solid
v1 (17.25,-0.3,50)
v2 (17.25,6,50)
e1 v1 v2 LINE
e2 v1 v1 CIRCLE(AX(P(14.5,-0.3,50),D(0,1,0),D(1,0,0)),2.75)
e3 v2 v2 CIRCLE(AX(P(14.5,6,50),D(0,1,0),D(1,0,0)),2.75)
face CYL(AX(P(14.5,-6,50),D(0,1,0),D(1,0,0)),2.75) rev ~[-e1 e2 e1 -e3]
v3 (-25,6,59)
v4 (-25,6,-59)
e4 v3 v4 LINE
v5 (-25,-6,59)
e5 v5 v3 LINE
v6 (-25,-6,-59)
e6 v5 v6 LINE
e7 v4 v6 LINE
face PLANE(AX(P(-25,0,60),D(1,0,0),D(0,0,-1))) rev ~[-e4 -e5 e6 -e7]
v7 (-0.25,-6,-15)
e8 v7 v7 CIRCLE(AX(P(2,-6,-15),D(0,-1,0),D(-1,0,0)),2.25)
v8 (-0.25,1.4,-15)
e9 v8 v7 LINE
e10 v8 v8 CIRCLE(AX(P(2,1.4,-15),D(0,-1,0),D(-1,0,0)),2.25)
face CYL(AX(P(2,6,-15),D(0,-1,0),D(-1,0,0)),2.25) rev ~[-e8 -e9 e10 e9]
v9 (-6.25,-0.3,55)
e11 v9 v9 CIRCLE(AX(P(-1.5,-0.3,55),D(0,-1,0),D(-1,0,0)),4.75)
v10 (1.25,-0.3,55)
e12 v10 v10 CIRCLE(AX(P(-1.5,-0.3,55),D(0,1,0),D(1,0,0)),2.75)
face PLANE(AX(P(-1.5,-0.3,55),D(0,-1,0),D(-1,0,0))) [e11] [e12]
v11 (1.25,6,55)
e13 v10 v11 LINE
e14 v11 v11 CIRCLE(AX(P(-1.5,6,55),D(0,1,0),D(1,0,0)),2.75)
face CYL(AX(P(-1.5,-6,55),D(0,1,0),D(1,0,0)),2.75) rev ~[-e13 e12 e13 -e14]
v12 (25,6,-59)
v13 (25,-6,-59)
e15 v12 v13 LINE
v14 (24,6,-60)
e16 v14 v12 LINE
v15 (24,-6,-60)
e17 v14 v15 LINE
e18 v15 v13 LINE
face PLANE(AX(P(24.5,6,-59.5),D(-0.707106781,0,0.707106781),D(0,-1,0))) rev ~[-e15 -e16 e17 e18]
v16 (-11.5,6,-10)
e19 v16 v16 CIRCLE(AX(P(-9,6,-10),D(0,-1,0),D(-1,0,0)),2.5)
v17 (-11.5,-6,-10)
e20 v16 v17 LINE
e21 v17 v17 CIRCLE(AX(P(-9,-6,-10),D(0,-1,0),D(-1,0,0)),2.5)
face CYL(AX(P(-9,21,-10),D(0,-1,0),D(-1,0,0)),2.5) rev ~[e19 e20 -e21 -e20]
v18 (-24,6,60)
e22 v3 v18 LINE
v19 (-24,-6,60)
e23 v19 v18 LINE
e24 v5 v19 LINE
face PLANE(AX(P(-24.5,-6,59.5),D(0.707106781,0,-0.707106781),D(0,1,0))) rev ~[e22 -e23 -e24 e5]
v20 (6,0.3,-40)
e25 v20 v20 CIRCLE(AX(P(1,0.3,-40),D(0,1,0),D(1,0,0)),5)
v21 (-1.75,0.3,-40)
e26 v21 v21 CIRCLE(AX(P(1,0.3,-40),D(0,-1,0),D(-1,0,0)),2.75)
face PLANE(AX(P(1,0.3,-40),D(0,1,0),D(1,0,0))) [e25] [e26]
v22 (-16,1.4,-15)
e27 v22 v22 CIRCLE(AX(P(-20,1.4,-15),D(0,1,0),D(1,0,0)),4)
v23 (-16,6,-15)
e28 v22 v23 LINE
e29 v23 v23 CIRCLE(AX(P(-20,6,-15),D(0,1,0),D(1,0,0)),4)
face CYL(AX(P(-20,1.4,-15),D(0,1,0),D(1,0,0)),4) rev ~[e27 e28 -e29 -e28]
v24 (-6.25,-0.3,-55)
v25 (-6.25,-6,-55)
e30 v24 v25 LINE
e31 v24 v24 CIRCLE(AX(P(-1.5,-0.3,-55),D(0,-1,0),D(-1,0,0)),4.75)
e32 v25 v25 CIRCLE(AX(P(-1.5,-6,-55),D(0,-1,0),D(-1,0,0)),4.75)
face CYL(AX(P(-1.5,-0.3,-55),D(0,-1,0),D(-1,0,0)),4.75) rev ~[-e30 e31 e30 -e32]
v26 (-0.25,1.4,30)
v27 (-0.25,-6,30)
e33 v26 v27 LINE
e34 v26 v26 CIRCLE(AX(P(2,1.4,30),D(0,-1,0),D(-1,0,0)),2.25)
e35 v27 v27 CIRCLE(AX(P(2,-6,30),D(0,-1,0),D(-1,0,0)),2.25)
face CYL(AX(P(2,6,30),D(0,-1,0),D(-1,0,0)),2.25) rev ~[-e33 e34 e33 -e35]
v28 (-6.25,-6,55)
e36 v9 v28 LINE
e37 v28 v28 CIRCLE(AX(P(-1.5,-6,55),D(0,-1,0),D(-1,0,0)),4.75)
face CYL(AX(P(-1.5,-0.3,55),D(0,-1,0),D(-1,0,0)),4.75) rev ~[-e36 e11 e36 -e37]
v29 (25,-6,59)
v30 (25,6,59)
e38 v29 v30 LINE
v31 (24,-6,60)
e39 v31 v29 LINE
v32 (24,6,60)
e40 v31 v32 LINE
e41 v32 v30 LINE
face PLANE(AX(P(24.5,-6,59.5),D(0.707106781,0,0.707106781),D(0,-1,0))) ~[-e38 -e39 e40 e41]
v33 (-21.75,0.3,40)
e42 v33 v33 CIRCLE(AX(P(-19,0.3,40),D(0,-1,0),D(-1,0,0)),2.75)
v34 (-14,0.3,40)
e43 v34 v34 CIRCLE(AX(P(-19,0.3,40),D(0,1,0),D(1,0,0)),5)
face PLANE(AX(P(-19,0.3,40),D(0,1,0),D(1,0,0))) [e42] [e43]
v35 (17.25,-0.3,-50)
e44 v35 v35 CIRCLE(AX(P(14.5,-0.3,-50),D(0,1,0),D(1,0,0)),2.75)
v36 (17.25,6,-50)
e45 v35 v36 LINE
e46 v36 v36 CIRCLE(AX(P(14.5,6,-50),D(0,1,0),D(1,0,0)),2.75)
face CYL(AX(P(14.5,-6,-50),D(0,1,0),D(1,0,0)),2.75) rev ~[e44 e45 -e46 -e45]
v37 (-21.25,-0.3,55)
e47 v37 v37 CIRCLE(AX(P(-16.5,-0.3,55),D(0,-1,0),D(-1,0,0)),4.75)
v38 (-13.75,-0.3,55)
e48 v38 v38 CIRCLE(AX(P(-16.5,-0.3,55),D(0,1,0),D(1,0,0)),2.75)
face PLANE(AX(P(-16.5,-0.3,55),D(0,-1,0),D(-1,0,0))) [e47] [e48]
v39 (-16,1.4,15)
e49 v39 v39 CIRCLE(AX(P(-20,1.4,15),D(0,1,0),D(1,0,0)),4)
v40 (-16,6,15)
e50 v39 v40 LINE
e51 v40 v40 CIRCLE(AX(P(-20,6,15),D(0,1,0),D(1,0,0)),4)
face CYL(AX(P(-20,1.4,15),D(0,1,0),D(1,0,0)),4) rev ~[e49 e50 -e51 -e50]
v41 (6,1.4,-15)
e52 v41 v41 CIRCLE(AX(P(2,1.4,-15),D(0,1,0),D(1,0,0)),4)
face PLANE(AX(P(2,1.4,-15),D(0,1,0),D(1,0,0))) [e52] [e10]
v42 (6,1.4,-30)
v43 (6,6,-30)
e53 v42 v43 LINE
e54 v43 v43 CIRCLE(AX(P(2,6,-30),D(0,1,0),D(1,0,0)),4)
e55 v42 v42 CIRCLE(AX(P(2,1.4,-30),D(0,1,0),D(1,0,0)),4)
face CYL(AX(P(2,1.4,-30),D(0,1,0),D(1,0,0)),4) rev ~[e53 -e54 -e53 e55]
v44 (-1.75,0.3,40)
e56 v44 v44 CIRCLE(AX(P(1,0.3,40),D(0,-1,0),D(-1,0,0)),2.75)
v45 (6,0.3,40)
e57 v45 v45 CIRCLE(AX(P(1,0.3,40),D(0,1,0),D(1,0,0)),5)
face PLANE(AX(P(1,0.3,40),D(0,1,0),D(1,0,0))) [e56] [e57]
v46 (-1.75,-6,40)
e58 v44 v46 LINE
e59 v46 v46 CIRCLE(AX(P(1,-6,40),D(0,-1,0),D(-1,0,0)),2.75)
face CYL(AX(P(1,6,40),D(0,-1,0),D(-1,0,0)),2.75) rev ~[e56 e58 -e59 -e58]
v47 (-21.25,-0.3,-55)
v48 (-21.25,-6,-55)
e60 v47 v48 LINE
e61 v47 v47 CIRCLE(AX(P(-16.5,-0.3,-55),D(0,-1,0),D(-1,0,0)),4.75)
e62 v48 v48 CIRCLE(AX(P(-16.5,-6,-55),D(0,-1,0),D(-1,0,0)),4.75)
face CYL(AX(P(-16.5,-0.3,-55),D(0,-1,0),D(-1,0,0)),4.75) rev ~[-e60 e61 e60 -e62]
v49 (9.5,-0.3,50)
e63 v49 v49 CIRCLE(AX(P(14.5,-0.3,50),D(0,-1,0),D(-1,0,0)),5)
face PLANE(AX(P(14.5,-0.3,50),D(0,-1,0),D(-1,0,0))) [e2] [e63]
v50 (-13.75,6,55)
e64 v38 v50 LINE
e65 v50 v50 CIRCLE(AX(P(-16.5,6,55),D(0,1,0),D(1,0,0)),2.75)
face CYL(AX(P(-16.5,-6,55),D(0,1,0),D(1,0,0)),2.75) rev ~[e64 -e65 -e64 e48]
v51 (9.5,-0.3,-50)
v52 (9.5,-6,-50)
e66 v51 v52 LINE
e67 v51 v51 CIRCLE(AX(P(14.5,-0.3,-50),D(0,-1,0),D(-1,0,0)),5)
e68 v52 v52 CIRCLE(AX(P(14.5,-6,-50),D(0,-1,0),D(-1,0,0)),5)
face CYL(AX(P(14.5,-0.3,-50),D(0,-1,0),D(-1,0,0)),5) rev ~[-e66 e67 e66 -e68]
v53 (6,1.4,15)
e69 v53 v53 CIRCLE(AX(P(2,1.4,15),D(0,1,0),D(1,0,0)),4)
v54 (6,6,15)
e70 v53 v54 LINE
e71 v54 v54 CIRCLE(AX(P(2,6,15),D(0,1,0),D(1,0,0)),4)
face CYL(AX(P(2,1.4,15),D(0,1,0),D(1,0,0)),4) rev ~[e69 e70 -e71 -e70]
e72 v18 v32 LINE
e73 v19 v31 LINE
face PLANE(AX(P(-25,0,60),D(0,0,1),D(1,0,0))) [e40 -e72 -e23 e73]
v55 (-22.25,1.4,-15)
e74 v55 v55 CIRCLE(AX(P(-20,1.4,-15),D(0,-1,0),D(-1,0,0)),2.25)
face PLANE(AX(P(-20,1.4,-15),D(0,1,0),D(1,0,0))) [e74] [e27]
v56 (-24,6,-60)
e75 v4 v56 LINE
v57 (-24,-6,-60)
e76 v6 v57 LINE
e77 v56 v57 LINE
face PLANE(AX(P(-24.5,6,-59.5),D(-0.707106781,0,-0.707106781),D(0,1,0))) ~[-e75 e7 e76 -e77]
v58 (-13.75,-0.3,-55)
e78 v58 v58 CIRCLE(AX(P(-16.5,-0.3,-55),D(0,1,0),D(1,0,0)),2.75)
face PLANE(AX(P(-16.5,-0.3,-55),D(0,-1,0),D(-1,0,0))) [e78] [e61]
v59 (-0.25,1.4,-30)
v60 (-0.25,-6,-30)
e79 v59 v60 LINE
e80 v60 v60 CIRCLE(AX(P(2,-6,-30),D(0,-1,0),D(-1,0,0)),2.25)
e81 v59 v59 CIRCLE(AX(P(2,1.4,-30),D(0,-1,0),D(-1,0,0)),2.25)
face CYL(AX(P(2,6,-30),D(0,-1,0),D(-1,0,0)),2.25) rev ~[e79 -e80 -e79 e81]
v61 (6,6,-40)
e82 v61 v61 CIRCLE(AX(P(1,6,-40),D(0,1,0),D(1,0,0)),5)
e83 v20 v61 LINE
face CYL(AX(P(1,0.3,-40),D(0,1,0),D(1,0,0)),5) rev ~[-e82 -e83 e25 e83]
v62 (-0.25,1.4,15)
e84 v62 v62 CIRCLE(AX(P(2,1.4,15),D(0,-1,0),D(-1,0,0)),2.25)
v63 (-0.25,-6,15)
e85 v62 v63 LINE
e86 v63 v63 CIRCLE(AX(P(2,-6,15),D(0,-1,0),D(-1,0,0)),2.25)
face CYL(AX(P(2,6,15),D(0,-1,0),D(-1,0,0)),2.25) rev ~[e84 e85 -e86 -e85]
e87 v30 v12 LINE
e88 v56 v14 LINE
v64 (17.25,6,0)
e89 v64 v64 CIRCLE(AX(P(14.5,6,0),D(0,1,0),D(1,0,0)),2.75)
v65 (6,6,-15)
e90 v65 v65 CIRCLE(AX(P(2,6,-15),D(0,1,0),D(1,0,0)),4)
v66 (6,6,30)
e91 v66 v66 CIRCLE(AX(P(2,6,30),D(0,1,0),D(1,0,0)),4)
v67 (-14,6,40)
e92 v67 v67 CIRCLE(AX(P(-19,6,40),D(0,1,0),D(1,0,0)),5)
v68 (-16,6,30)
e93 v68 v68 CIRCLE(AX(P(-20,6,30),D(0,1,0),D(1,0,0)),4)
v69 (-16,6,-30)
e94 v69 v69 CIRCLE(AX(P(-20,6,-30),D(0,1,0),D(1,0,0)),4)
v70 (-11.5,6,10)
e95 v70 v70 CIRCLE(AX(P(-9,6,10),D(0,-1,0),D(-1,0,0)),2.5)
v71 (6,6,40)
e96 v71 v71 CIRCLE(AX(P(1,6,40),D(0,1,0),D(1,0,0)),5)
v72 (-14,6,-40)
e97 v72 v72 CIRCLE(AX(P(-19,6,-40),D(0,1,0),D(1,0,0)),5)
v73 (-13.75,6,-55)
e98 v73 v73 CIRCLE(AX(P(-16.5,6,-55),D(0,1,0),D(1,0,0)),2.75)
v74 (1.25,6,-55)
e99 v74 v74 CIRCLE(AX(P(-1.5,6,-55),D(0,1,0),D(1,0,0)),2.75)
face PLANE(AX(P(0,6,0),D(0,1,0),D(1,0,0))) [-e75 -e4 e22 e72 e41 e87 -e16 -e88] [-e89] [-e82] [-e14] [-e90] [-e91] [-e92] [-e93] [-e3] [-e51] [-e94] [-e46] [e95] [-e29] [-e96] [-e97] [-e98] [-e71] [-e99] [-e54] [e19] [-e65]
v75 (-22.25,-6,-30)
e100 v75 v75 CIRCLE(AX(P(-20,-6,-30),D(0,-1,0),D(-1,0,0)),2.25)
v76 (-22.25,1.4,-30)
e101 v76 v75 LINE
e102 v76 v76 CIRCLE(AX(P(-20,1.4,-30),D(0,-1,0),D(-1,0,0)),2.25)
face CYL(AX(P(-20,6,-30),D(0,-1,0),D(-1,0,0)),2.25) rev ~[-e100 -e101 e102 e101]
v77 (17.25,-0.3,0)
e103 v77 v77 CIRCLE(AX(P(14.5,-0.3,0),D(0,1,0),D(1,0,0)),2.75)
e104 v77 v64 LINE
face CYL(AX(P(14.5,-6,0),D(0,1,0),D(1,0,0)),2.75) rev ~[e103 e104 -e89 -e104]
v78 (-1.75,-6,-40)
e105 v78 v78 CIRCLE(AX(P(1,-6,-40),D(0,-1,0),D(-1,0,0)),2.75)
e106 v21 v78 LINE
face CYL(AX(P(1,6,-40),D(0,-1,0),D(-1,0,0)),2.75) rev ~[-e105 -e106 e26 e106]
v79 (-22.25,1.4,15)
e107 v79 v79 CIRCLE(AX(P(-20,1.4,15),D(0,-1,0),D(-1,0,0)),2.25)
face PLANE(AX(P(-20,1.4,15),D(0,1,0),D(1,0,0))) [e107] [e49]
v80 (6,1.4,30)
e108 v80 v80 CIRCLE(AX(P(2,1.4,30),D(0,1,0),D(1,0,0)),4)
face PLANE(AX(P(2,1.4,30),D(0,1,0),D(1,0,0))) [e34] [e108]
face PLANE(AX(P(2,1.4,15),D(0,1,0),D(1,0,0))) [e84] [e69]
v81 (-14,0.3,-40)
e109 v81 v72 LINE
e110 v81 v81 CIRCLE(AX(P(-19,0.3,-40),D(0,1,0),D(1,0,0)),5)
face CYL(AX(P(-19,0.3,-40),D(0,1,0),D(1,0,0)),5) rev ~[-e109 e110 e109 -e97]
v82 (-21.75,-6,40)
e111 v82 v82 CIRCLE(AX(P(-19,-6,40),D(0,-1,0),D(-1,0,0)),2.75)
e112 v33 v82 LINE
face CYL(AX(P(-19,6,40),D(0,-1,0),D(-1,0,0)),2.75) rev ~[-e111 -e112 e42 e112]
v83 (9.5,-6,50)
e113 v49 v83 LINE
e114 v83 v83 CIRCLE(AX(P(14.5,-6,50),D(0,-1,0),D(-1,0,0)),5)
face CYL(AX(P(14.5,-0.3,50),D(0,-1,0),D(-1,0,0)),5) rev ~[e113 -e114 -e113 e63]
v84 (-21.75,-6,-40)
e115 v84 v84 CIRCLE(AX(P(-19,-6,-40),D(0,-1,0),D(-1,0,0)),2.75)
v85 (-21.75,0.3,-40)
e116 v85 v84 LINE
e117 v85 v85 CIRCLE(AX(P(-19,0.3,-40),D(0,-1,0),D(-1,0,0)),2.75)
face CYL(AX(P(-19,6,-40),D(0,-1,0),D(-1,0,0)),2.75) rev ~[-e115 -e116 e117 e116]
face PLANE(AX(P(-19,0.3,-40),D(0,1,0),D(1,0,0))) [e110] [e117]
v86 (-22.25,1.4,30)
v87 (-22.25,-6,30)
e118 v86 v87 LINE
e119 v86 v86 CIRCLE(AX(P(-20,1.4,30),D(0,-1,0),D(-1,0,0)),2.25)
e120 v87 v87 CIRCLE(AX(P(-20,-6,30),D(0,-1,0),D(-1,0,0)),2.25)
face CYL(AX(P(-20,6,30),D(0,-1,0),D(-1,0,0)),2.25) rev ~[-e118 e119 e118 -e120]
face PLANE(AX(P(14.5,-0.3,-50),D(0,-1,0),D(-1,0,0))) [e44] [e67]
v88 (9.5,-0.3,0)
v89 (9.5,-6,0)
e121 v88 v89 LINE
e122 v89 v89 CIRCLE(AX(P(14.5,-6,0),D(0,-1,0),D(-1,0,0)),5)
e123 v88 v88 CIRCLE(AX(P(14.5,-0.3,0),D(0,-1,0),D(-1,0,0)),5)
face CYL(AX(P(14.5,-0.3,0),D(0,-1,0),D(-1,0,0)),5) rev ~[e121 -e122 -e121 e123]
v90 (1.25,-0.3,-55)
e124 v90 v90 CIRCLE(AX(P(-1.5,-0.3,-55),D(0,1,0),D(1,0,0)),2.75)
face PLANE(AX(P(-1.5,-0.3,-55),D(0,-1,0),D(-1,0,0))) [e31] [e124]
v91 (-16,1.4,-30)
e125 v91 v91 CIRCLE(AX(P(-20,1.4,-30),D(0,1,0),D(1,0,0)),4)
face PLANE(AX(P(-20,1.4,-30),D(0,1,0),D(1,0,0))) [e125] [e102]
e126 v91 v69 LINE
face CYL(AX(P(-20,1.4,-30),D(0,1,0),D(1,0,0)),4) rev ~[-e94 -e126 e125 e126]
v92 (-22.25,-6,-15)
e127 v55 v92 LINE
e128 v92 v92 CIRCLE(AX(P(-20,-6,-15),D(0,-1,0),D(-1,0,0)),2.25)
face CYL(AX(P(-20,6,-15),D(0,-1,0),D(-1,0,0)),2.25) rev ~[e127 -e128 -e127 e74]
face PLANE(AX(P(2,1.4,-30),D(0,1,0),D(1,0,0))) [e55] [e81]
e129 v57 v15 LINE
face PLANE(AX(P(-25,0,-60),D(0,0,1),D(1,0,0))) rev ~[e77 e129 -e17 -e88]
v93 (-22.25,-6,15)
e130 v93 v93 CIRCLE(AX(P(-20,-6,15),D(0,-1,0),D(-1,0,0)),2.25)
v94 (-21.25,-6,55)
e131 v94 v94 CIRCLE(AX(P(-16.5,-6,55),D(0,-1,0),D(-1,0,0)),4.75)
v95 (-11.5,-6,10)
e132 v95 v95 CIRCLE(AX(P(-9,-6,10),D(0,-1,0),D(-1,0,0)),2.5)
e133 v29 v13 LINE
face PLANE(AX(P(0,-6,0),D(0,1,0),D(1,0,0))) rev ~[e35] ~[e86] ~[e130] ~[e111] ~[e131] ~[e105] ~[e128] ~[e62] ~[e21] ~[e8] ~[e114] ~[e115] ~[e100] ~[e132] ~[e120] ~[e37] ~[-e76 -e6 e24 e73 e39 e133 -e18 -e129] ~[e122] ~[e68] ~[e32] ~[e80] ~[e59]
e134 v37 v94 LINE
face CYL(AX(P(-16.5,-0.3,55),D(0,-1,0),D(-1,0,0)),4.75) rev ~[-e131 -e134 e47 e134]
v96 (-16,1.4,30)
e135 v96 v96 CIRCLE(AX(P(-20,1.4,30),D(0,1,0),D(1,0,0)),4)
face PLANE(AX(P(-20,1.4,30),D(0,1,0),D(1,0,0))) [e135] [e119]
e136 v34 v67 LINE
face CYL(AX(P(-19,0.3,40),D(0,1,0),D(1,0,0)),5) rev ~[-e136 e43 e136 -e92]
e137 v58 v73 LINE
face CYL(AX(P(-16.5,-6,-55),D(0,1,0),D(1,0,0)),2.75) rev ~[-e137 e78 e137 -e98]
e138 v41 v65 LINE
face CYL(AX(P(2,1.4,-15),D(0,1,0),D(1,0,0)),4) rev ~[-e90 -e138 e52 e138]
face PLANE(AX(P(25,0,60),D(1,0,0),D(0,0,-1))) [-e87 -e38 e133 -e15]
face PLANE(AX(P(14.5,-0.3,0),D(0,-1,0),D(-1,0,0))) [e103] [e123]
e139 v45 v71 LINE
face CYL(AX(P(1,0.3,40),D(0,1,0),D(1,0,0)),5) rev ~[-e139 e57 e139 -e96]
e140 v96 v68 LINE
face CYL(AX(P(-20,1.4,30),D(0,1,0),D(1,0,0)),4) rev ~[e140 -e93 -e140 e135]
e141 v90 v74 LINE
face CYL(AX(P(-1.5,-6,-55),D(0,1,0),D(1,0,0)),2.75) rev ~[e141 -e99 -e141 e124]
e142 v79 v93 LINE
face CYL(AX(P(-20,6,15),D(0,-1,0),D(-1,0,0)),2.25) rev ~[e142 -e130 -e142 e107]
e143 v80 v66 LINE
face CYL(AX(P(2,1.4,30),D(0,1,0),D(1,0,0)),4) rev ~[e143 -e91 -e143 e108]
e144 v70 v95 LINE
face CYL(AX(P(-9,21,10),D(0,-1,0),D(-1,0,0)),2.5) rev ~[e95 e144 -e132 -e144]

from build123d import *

# Parameters (mm, degrees)
SKETCH_1_W                   = 50
SKETCH_1_H                   = 120
EXTRUDE_1_DEPTH              = 6
HOLE_WIZARD_M4_1_D           = 4.5
HOLE_WIZARD_M4_1_CBORE_D     = 8
HOLE_WIZARD_M4_1_CBORE_DEPTH = 4.6
HOLE_WIZARD_M5_3_D           = 5.5
HOLE_WIZARD_M5_3_CBORE_D     = 9.5
HOLE_WIZARD_M5_3_CBORE_DEPTH = 5.7
HOLE_WIZARD_M6_1_D           = 5
HOLE_WIZARD_M6_1_DEPTH       = 15
HOLE_WIZARD_M6_1_TIP         = 1.502151548
HOLE_WIZARD_M5_1_D           = 5.5
HOLE_WIZARD_M5_1_CBORE_D     = 10
HOLE_WIZARD_M5_1_CBORE_DEPTH = 5.7
CHAMFER_1_SIZE               = 1
HOLE_WIZARD_M5_4_D           = 5.5
HOLE_WIZARD_M5_4_CBORE_D     = 10
HOLE_WIZARD_M5_4_CBORE_DEPTH = 5.7


with BuildPart() as part:
    # 草图1 → 凸台-拉伸1 (new, symmetric)
    with BuildSketch(Plane(origin=(0, 0, 0), x_dir=(1, 0, 0), z_dir=(0, 1, 0))):
        Rectangle(SKETCH_1_W, SKETCH_1_H)
    extrude(amount=EXTRUDE_1_DEPTH, both=True)

    # M4 六角圆柱头螺钉的柱形沉头孔1 (through all)
    with Locations(Plane(origin=(0, 6, 0), x_dir=(1, 0, 0), z_dir=(0, 1, 0))):
        with Locations((2, 15), (-20, 30), (2, 30), (-20, 15), (-20, -15), (2, -30), (-20, -30), (2, -15)):
            CounterBoreHole(HOLE_WIZARD_M4_1_D / 2, HOLE_WIZARD_M4_1_CBORE_D / 2, HOLE_WIZARD_M4_1_CBORE_DEPTH)

    # M5 六角圆柱头螺钉的柱形沉头孔3 (through all)
    with Locations(Plane(origin=(0, -6, 0), x_dir=(-1, 0, 0), z_dir=(0, -1, 0))):
        with Locations((16.499999999, -55), (1.500000001, -55), (1.500000001, 55), (16.499999999, 55)):
            CounterBoreHole(HOLE_WIZARD_M5_3_D / 2, HOLE_WIZARD_M5_3_CBORE_D / 2, HOLE_WIZARD_M5_3_CBORE_DEPTH)

    # M6 螺纹孔1
    with Locations(Plane(origin=(0, 6, 0), x_dir=(1, 0, 0), z_dir=(0, 1, 0))):
        with Locations((-9, 10), (-9, -10)):
            Hole(HOLE_WIZARD_M6_1_D / 2, depth=HOLE_WIZARD_M6_1_DEPTH)
            with Locations((0, 0, -(HOLE_WIZARD_M6_1_DEPTH + HOLE_WIZARD_M6_1_TIP / 2))):  # 118° drill point
                Cone(0, HOLE_WIZARD_M6_1_D / 2, HOLE_WIZARD_M6_1_TIP, mode=Mode.SUBTRACT)

    # M5 六角圆柱头螺钉的柱形沉头孔1 (through all)
    with Locations(Plane(origin=(0, 6, 0), x_dir=(1, 0, 0), z_dir=(0, 1, 0))):
        with Locations((1, 40), (1, -40), (-19, -40), (-19, 40)):
            CounterBoreHole(HOLE_WIZARD_M5_1_D / 2, HOLE_WIZARD_M5_1_CBORE_D / 2, HOLE_WIZARD_M5_1_CBORE_DEPTH)

    # 倒角1
    chamfer_1_edges = [part.edges().sort_by_distance(p)[0] for p in [
        (25, 0, 60),
        (-25, 0, 60),
        (-25, 0, -60),
        (25, 0, -60),
    ]]
    chamfer(chamfer_1_edges, length=CHAMFER_1_SIZE)

    # M5 六角圆柱头螺钉的柱形沉头孔4 (through all)
    with Locations(Plane(origin=(0, -6, 0), x_dir=(-1, 0, 0), z_dir=(0, -1, 0))):
        with Locations((-14.5, 50), (-14.5, 0), (-14.5, -50)):
            CounterBoreHole(HOLE_WIZARD_M5_4_D / 2, HOLE_WIZARD_M5_4_CBORE_D / 2, HOLE_WIZARD_M5_4_CBORE_DEPTH)


solid = part.part
